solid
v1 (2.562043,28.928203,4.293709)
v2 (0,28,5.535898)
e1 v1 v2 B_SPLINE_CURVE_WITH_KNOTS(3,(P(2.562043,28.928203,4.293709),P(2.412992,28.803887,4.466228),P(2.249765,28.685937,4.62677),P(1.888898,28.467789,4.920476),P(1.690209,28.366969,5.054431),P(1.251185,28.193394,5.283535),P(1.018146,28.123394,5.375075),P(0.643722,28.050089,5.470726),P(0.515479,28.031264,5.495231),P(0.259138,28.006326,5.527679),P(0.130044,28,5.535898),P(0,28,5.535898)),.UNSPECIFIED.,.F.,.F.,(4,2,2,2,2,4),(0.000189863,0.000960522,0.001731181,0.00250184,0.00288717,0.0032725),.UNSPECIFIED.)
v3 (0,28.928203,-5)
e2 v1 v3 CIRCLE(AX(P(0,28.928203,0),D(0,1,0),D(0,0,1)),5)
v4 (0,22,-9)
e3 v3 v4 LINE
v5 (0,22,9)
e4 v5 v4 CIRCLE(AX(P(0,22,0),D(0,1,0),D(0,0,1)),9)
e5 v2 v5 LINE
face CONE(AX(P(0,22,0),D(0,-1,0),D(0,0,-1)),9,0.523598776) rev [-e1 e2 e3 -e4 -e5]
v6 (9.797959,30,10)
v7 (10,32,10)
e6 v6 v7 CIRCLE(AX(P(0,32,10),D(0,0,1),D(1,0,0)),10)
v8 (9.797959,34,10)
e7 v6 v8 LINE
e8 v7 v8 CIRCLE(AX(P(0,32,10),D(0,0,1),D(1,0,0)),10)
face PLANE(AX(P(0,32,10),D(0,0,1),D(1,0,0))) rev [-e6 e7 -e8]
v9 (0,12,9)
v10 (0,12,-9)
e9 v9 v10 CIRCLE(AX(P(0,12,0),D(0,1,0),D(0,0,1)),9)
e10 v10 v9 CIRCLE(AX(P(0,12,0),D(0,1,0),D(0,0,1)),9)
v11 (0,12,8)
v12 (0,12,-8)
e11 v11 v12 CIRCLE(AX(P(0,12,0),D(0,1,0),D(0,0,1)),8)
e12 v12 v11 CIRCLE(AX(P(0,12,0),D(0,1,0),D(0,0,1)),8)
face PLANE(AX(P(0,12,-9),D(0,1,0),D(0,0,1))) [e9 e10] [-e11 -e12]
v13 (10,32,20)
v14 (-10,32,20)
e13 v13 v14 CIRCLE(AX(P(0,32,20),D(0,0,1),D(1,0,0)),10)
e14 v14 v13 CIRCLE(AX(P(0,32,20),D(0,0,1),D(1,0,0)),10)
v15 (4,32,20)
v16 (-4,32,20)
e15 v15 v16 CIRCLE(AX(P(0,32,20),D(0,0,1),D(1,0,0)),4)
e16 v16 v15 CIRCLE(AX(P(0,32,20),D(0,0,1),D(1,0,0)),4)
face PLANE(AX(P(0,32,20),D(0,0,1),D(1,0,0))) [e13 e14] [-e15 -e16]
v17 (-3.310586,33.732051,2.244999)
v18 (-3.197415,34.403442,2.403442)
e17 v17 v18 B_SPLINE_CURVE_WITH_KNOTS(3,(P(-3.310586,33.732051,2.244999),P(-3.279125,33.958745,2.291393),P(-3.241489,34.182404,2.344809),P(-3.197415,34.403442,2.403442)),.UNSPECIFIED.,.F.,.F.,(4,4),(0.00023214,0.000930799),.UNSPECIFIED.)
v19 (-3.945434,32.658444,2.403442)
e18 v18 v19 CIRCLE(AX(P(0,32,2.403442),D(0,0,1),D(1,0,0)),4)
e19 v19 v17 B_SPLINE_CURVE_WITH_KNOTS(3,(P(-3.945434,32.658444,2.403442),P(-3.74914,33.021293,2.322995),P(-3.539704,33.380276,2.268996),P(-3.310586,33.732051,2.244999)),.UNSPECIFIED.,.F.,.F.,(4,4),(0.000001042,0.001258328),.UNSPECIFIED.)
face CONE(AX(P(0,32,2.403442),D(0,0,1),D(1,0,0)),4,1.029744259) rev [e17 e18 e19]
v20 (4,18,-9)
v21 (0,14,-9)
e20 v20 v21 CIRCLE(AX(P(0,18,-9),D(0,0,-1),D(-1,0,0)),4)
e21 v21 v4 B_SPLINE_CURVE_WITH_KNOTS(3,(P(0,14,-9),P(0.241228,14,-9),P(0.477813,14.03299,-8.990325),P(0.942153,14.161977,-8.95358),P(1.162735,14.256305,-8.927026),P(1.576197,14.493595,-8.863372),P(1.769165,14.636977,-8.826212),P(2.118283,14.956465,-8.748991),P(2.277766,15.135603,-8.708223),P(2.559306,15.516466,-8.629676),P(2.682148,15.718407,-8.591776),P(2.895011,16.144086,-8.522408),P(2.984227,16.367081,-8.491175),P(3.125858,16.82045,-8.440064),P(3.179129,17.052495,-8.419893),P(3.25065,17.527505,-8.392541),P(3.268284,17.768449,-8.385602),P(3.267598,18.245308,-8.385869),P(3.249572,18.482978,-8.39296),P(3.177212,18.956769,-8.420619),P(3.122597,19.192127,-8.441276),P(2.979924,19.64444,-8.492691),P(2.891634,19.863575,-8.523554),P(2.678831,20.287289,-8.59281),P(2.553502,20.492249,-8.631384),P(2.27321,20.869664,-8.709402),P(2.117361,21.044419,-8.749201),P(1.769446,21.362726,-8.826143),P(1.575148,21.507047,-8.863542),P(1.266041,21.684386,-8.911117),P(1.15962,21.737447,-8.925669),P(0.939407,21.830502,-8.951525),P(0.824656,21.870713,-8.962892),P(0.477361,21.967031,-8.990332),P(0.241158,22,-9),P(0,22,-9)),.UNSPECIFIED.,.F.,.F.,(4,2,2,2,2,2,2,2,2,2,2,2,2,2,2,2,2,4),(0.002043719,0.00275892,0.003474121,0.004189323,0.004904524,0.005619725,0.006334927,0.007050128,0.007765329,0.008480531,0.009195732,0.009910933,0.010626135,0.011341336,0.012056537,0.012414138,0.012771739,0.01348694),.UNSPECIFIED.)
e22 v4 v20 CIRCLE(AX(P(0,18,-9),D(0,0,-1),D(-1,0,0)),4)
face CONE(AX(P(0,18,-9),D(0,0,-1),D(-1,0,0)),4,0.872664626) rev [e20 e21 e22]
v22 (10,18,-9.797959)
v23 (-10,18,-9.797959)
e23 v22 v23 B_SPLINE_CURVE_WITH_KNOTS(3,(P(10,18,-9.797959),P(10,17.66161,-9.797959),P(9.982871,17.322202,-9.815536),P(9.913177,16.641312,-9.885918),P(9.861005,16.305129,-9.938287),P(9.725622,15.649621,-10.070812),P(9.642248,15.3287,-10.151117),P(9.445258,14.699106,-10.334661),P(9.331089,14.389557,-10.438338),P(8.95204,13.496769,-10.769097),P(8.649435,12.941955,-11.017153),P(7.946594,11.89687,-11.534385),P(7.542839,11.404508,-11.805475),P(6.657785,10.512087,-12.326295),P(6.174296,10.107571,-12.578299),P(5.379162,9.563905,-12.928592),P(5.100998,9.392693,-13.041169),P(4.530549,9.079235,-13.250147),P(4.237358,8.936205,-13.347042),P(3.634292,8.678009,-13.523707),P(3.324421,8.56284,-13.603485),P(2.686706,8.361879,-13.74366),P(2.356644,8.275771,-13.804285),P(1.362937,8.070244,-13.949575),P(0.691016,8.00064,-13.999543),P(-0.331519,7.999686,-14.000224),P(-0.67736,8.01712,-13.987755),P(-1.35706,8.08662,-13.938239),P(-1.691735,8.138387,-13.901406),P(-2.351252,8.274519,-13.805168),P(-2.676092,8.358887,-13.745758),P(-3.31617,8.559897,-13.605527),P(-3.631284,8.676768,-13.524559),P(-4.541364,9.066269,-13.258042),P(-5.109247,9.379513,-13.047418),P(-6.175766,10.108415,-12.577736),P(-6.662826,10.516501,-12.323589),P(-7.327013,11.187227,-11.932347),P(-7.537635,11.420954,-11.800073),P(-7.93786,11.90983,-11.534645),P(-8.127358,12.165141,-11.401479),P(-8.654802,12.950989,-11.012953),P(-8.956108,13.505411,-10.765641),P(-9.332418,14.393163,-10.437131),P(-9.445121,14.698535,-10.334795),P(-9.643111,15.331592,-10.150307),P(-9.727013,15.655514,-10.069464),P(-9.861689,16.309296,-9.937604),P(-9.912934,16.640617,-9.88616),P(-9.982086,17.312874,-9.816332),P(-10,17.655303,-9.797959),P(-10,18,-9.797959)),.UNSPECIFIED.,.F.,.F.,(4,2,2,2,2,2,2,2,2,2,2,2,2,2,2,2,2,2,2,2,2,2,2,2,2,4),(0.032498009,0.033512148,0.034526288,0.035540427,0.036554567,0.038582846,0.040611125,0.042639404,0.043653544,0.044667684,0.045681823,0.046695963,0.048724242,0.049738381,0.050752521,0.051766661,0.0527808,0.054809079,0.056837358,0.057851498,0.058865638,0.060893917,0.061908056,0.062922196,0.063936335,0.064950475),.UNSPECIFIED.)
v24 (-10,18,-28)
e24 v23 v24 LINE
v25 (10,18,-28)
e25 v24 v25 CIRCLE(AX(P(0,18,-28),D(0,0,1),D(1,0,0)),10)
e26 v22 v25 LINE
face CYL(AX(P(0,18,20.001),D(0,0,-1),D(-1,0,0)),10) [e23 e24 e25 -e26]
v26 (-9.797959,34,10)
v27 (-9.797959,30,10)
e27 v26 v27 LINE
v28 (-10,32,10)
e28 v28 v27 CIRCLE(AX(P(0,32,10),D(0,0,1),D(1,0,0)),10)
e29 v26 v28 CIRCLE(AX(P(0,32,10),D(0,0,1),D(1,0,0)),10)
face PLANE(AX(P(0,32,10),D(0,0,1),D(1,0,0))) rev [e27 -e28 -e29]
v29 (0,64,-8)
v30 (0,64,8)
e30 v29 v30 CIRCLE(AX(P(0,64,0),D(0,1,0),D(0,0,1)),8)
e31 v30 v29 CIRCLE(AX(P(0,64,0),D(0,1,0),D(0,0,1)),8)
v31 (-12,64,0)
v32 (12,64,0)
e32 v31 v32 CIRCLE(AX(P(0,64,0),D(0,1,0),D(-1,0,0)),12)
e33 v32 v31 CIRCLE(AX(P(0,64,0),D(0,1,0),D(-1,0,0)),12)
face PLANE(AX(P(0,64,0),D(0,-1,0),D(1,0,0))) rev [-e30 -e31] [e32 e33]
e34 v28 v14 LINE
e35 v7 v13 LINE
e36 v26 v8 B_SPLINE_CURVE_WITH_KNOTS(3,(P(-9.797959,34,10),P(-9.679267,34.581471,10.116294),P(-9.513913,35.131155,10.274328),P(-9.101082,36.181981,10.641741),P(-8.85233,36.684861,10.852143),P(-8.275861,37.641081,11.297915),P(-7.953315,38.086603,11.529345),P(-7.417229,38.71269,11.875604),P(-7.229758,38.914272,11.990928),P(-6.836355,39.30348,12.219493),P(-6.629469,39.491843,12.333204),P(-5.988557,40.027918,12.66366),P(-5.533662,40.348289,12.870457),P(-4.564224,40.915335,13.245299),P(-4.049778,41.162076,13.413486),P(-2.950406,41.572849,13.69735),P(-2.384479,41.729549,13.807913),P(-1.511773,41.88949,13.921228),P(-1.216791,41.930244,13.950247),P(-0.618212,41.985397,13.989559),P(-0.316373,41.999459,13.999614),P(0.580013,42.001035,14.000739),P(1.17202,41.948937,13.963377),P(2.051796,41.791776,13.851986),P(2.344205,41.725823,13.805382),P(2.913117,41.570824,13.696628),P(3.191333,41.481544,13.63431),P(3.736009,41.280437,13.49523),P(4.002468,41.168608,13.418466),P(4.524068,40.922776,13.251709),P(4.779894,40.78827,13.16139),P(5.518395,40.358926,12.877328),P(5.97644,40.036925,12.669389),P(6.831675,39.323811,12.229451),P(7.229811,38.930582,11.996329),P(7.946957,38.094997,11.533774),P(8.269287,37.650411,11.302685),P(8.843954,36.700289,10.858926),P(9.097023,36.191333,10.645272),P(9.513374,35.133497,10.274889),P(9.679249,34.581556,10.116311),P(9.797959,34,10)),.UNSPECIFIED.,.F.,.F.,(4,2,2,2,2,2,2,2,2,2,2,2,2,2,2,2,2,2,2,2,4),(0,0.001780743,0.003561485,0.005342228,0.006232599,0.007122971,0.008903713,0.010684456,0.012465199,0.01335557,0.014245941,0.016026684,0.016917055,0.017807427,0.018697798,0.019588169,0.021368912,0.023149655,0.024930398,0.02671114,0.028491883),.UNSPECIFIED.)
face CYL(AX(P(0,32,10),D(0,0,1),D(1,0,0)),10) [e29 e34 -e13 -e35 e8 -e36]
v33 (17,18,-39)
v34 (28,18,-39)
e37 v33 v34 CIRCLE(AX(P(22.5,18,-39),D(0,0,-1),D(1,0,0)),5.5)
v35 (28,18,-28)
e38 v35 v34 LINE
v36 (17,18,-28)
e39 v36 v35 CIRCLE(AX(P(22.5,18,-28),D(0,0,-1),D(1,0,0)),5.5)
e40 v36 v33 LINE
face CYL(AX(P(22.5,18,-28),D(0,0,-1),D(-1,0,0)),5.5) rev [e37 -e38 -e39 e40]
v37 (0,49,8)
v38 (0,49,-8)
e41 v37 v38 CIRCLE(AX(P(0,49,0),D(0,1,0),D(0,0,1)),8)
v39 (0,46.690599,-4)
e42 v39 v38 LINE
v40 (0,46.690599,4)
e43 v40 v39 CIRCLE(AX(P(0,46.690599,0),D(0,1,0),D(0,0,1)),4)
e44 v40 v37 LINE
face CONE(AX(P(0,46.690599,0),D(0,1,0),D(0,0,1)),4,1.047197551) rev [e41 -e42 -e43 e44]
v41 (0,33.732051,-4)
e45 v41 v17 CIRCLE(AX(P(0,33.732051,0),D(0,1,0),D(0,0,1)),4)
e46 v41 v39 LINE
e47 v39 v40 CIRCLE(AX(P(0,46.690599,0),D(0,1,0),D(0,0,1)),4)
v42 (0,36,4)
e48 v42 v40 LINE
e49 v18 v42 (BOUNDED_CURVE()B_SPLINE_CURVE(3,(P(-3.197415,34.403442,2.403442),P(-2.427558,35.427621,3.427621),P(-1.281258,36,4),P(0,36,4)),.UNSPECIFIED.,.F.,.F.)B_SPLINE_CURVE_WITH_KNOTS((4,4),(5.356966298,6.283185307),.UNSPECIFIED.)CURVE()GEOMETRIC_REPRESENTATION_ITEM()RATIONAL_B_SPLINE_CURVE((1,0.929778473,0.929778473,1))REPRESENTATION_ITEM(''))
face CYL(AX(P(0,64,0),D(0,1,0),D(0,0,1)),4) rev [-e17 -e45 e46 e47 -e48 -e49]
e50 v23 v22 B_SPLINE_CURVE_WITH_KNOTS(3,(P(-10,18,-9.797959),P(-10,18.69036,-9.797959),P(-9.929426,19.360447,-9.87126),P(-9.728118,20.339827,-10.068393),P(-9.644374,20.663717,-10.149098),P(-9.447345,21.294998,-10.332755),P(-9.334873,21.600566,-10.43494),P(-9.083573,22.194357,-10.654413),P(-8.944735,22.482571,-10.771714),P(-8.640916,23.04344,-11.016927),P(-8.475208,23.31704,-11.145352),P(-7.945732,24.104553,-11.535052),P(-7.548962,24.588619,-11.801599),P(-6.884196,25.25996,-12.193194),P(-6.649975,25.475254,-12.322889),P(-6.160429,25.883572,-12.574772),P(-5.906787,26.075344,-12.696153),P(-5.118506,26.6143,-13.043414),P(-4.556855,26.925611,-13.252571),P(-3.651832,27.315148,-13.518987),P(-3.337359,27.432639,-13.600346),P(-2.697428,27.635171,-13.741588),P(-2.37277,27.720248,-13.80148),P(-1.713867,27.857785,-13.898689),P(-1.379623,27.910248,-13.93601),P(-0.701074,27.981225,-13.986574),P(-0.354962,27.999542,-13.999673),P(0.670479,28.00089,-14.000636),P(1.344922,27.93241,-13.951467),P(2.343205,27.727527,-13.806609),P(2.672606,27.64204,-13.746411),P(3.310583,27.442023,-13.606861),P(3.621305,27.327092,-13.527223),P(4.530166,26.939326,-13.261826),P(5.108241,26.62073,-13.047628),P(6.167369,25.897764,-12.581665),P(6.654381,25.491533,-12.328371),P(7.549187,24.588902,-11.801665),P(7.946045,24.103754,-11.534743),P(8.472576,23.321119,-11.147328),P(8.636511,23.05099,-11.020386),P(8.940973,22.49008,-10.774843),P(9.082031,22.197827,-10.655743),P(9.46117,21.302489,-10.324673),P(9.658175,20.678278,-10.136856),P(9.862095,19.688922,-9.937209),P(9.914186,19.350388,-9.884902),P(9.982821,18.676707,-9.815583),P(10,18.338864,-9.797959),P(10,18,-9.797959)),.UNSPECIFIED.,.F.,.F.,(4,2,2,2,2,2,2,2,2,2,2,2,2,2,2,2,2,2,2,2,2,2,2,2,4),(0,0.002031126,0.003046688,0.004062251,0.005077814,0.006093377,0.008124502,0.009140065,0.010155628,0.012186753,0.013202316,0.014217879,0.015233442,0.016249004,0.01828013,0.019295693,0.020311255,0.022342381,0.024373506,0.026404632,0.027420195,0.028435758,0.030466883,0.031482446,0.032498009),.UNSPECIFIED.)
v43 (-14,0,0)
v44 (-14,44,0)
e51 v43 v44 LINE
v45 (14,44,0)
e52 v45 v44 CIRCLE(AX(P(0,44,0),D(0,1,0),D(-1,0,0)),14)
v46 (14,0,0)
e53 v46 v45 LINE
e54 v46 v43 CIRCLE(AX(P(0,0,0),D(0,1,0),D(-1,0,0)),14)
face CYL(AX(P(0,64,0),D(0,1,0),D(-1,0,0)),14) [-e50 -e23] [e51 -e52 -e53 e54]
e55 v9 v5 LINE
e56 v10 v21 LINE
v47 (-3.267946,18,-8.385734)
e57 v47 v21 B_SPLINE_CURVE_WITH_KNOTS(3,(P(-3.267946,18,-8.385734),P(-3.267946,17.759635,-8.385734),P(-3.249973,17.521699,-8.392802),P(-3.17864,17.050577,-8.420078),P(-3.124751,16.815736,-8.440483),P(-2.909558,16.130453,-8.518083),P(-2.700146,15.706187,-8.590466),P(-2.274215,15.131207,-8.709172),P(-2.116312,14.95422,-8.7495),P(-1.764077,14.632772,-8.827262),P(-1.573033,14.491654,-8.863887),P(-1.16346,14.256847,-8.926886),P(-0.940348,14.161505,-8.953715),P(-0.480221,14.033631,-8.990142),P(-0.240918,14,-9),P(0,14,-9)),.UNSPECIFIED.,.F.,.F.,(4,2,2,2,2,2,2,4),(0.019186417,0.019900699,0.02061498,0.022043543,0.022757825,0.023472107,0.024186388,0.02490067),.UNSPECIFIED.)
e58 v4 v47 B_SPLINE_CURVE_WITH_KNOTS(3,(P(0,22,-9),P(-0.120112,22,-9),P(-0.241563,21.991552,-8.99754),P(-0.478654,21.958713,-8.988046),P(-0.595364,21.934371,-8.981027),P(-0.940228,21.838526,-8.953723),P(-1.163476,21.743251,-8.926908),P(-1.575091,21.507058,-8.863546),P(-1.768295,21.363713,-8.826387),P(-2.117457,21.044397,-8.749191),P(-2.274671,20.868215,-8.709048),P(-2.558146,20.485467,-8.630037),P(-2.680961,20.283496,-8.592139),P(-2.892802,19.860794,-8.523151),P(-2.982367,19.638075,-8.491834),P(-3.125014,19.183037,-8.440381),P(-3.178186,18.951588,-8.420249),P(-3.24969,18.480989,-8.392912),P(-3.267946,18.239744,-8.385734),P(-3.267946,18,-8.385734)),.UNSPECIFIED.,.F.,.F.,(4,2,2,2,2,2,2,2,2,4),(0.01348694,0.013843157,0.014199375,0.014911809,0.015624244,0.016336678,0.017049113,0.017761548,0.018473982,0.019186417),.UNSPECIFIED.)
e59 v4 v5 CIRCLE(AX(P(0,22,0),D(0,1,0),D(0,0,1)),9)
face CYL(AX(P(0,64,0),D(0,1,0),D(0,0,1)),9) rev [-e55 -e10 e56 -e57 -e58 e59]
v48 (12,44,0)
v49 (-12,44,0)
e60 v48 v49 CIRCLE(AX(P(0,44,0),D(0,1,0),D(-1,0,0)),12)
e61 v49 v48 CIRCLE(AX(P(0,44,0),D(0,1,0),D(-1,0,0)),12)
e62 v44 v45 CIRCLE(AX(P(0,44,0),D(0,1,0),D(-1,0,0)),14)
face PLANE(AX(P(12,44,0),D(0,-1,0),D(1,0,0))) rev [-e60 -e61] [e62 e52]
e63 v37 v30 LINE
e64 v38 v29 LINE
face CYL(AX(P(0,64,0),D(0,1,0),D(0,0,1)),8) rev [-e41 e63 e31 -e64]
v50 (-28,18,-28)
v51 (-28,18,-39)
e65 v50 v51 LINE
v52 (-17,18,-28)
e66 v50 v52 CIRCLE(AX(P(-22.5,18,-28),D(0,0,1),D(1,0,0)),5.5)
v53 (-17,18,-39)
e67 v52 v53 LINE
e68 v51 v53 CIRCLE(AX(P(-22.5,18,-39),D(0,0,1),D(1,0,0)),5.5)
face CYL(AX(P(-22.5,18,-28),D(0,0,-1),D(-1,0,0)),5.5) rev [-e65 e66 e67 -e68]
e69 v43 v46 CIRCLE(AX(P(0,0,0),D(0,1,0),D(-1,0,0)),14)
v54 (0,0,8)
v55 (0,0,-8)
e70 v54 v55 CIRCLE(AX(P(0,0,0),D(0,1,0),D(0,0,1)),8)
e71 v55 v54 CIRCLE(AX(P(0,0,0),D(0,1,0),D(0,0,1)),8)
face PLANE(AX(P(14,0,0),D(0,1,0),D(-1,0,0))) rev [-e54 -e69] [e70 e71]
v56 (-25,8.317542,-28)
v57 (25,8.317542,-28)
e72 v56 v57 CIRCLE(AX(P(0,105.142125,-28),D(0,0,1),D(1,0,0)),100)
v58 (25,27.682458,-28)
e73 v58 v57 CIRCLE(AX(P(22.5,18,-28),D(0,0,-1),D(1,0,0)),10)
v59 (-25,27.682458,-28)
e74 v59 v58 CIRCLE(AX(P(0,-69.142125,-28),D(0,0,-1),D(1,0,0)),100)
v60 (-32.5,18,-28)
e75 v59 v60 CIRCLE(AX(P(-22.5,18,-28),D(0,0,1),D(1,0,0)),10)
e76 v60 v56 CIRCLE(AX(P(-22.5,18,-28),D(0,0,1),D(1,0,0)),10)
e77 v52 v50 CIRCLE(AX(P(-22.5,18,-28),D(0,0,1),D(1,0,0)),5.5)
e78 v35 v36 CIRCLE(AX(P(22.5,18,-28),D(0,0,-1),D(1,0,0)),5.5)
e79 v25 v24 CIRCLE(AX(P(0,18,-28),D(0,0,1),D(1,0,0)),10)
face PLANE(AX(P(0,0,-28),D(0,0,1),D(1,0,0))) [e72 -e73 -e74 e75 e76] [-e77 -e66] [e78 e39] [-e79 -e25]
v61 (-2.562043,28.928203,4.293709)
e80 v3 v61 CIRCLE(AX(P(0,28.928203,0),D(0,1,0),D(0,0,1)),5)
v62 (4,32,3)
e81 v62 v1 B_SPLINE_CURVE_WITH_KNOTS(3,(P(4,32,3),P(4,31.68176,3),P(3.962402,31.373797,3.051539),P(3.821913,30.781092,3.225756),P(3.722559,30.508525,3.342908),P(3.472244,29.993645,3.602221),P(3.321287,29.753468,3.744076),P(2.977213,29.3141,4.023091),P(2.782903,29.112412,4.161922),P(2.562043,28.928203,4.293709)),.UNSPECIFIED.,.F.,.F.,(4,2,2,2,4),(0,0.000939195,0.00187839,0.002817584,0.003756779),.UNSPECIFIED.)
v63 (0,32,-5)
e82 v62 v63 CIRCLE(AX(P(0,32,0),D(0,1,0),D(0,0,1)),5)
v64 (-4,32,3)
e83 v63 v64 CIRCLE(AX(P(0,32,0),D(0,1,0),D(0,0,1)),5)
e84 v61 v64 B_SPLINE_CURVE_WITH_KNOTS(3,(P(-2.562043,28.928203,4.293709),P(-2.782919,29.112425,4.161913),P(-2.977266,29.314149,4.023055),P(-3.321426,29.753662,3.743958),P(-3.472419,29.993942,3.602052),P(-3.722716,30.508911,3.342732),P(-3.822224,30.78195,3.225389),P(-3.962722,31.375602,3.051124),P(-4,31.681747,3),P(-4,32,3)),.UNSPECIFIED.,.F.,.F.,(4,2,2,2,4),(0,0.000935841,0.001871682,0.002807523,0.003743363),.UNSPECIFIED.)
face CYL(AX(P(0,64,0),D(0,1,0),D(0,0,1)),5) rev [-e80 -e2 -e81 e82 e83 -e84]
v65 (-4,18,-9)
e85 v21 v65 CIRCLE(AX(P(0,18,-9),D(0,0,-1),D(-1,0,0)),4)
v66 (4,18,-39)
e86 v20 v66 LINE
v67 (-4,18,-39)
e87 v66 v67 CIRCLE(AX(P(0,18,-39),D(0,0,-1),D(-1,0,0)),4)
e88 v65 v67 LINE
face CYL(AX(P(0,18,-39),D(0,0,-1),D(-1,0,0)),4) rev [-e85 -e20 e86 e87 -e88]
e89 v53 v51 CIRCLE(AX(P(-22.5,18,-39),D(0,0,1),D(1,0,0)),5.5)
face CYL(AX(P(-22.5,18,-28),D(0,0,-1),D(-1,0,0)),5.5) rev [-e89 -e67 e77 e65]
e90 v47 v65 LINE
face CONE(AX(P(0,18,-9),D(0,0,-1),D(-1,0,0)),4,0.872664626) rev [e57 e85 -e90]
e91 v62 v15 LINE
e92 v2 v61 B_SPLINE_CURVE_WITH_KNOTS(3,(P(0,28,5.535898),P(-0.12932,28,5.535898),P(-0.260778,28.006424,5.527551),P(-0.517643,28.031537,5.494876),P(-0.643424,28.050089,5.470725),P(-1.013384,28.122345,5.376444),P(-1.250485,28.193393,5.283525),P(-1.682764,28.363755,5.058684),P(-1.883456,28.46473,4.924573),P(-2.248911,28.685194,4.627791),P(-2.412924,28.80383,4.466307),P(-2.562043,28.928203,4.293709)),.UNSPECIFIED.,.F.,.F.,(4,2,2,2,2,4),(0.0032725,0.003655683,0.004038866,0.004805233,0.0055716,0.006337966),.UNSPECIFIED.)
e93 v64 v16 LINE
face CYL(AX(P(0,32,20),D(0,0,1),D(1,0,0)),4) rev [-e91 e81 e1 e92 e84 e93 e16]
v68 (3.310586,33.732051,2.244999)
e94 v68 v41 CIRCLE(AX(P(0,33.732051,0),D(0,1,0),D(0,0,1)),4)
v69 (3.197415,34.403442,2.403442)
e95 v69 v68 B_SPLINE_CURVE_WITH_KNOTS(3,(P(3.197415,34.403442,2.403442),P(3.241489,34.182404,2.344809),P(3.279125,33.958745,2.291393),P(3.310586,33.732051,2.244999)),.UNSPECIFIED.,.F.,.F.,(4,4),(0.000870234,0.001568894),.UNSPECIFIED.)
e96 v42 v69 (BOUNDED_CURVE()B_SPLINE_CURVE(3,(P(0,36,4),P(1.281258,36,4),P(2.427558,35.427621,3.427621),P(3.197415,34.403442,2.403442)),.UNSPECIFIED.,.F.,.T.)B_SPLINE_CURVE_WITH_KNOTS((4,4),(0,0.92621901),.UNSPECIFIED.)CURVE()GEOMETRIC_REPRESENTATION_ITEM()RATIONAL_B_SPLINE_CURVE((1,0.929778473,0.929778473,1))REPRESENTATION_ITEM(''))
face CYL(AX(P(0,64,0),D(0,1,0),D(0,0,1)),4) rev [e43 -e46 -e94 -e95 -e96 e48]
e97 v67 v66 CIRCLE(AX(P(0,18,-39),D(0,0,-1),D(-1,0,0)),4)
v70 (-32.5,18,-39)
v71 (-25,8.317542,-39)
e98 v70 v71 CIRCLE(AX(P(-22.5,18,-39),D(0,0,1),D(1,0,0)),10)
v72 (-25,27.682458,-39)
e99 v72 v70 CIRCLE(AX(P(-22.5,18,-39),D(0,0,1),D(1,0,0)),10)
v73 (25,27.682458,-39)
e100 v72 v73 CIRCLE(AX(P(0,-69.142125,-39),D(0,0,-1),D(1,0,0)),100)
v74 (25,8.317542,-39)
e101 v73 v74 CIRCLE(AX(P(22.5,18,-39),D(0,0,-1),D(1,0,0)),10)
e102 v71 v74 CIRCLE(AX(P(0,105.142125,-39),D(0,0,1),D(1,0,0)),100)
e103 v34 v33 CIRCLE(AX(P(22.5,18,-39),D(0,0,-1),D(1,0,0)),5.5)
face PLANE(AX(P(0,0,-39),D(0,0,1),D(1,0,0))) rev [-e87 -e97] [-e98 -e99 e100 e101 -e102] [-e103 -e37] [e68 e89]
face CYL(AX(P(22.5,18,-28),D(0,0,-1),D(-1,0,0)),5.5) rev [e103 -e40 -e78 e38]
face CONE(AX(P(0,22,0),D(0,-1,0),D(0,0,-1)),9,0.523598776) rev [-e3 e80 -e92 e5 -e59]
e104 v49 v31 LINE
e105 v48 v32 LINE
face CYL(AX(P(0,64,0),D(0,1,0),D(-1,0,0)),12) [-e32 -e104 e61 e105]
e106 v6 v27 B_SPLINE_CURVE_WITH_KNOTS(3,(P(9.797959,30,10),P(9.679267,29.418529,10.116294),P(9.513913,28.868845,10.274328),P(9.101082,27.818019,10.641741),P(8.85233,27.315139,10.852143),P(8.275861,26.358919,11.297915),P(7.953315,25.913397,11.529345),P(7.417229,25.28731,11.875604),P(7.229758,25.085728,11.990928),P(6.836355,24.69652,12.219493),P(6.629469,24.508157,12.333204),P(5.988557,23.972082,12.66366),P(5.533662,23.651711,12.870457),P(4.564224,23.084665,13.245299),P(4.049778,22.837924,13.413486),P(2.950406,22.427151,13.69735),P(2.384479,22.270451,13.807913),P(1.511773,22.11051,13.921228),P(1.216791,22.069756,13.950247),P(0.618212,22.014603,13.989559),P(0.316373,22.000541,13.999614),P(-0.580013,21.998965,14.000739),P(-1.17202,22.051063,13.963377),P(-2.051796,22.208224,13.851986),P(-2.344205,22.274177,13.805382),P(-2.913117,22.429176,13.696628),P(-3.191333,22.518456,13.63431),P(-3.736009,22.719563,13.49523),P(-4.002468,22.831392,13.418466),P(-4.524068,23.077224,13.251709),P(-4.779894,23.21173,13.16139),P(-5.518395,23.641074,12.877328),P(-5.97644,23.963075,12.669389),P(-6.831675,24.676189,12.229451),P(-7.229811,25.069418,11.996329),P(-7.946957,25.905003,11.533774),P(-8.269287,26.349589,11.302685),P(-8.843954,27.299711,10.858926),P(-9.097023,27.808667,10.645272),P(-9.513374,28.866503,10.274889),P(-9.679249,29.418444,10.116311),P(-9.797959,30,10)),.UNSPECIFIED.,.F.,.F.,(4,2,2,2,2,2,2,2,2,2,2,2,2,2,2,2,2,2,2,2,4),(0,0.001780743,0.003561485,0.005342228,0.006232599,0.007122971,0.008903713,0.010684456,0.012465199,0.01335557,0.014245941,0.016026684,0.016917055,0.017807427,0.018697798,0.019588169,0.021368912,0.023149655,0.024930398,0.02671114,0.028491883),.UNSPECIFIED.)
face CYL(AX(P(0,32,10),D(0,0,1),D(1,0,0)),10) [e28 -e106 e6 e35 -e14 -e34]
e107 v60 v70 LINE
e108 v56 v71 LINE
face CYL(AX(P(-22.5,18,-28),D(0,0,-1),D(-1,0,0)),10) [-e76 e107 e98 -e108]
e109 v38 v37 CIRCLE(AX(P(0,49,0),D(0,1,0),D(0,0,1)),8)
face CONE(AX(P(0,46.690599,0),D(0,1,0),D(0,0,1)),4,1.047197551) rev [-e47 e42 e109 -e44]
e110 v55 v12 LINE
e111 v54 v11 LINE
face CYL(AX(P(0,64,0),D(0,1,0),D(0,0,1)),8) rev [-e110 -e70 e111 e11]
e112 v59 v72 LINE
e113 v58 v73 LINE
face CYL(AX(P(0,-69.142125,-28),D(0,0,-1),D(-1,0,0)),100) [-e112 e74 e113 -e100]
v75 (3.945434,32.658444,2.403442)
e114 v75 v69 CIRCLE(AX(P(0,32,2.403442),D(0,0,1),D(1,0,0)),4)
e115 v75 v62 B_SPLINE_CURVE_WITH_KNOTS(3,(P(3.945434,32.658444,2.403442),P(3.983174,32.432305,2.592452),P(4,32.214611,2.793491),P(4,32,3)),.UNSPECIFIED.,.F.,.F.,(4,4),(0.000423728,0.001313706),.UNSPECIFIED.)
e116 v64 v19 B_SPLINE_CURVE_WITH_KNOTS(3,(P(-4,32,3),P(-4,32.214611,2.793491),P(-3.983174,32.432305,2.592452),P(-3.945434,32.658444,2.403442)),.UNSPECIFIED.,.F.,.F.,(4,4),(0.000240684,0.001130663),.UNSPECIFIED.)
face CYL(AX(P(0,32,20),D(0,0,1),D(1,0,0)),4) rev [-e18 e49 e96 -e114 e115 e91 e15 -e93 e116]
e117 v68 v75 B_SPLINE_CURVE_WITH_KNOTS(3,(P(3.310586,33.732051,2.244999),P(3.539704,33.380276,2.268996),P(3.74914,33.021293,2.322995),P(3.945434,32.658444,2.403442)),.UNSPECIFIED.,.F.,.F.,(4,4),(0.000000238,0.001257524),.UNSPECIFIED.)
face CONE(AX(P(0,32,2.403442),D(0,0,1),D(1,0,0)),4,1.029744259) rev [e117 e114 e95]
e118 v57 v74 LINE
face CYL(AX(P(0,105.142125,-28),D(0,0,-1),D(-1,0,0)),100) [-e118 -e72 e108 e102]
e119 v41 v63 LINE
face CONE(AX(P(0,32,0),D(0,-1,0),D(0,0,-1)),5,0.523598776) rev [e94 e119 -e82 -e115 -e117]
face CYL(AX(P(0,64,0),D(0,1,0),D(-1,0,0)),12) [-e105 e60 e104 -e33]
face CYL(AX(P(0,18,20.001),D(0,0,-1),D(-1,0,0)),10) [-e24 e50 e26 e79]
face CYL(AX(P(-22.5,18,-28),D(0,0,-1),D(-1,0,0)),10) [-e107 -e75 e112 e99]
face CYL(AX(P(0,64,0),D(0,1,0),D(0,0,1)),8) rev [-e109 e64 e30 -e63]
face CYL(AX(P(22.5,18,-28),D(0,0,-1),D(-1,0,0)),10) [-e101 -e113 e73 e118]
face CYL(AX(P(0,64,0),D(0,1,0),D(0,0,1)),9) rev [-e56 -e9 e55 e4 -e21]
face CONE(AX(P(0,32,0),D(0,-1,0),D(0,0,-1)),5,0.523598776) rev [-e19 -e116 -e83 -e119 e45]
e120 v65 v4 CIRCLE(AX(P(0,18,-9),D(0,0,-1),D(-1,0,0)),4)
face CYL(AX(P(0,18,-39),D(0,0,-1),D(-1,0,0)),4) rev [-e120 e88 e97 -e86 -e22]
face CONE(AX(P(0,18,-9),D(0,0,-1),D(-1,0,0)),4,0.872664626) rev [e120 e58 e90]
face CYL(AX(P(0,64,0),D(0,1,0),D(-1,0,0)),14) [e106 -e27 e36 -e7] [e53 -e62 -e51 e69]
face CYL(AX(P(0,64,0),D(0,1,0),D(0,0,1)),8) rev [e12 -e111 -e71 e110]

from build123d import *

# Parameters (mm, degrees)
SIDE_PORT_BOSS_SKETCH_R            = 10
SIDE_PORT_BOSS_DEPTH               = 10
MOUNTING_EAR_SKETCH_R              = 5.5
MOUNTING_EAR_DEPTH                 = 11
EAR_HUB_BOSS_REACH                 = 88.35
EAR_HUB_BOSS_END_RADIUS            = 14
EAR_HUB_SKETCH_R                   = 10
EAR_HOLE_8_D                       = 8
EAR_HOLE_8_DEPTH                   = 30
EAR_HOLE_8_TIP                     = 3.356398525
SIDE_PORT_TAPPED_HOLE_M8X1_0_D     = 8
SIDE_PORT_TAPPED_HOLE_M8X1_0_DEPTH = 17.596557524
SIDE_PORT_TAPPED_HOLE_M8X1_0_TIP   = 2.403442476


with BuildPart() as part:
    # Main Body Profile Sketch → Main Body Revolve (revolve)
    with BuildSketch(Plane.XY, mode=Mode.PRIVATE) as main_body_revolve_sk:
        Polygon((0, 64), (12, 64), (12, 44), (14, 44), (14, 0), (0, 0), align=None)
    revolve(main_body_revolve_sk.sketch.rotate(Axis((0, 64, 0), (0, -1, 0)), 180), axis=Axis((0, 64, 0), (0, -1, 0)))

    # Side Port Boss Sketch → Side Port Boss (add)
    with BuildSketch(Plane.XY.offset(20)):
        with Locations((0, 32)):
            Circle(SIDE_PORT_BOSS_SKETCH_R)
    extrude(amount=-SIDE_PORT_BOSS_DEPTH)



with BuildPart() as body_2:
    # Mounting Ear Sketch → Mounting Ear (new body)
    # profile 1 of 6: a face of its own
    with BuildSketch(Plane.XY.offset(-39)):
        with BuildLine():
            Line((0, 14), (0, 5.14212529))
            ThreePointArc((0, 5.14212529), (12.600429248, 5.939155663), (25, 8.317541634))
            ThreePointArc((25, 8.317541634), (32.5, 18), (25, 27.682458366))
            ThreePointArc((25, 27.682458366), (12.600429248, 30.060844337), (0, 30.85787471))
            Line((0, 30.85787471), (0, 22))
            ThreePointArc((0, 22), (2.828427125, 20.828427125), (4, 18))
            ThreePointArc((4, 18), (2.828427125, 15.171572875), (0, 14))
        make_face()
        with Locations((22.5, 18)):
            Circle(MOUNTING_EAR_SKETCH_R, mode=Mode.SUBTRACT)
    # profile 2 of 6: a face of its own
    with BuildSketch(Plane.XY.offset(-39)):
        with BuildLine():
            ThreePointArc((-25, 8.317541634), (-12.600429248, 5.939155663), (0, 5.14212529))
            Line((0, 5.14212529), (0, 14))
            ThreePointArc((0, 14), (-4, 18), (0, 22))
            Line((0, 22), (0, 30.85787471))
            ThreePointArc((0, 30.85787471), (-12.600429248, 30.060844337), (-25, 27.682458366))
            ThreePointArc((-25, 27.682458366), (-32.5, 18), (-25, 8.317541634))
        make_face()
        with Locations((-22.5, 18)):
            Circle(MOUNTING_EAR_SKETCH_R, mode=Mode.SUBTRACT)
    # profile 3 of 6: a face of its own
    with BuildSketch(Plane.XY.offset(-39)):
        with BuildLine():
            ThreePointArc((0, 22), (-4, 18), (0, 14))
            Line((0, 14), (0, 22))
        make_face()
    # profile 4 of 6: a face of its own
    with BuildSketch(Plane.XY.offset(-39)):
        with BuildLine():
            Line((0, 22), (0, 14))
            ThreePointArc((0, 14), (2.828427125, 15.171572875), (4, 18))
            ThreePointArc((4, 18), (2.828427125, 20.828427125), (0, 22))
        make_face()
    # profile 5 of 6: a face of its own
    with BuildSketch(Plane.XY.offset(-39)):
        with BuildLine():
            ThreePointArc((0, 22), (-4, 18), (0, 14))
            Line((0, 14), (0, 22))
        make_face()
    # profile 6 of 6: a face of its own
    with BuildSketch(Plane.XY.offset(-39)):
        with BuildLine():
            Line((0, 22), (0, 14))
            ThreePointArc((0, 14), (2.828427125, 15.171572875), (4, 18))
            ThreePointArc((4, 18), (2.828427125, 20.828427125), (0, 22))
        make_face()
    extrude(amount=MOUNTING_EAR_DEPTH)


with BuildPart() as part_1:
    add(part.part)

    add(body_2.part)  # Ear Hub Boss merges body 2
    # Ear Hub Boss: up to this cylinder (the profile starts outside it)
    ear_hub_boss_end = Plane(origin=(0, 18, 0), z_dir=(0, 1, 0)) * Cylinder(EAR_HUB_BOSS_END_RADIUS, 205.7, mode=Mode.PRIVATE)
    # Ear Hub Sketch → Ear Hub Boss (add, up to the surface)
    with BuildSketch(Plane.XY.offset(-28), mode=Mode.PRIVATE) as ear_hub_boss_sk1:
        with Locations(Location((0, 18, 0), (0, 0, 180))):
            Circle(EAR_HUB_SKETCH_R)
    ear_hub_boss_tool1 = extrude(ear_hub_boss_sk1.sketch, amount=EAR_HUB_BOSS_REACH, mode=Mode.PRIVATE) - ear_hub_boss_end
    add(ear_hub_boss_tool1.solids().sort_by_distance((0, 18, -28))[0])

    # Bore Profile Sketch → Bore Revolve Cut (revolve, cut)
    with BuildSketch(Plane(origin=(0, 0, 0), x_dir=(0, 0, -1), z_dir=(1, 0, 0)), mode=Mode.PRIVATE) as bore_revolve_cut_sk:
        Polygon((0, 64), (8, 64), (8, 49), (4, 46.690598923), (4, 33.732050808), (5, 32), (5, 28.92820323), (9, 22), (9, 12), (8, 12), (8, 0), (0, 0), align=None)
    revolve(bore_revolve_cut_sk.sketch.rotate(Axis((0, 64, 0), (0, -1, 0)), 180), axis=Axis((0, 64, 0), (0, -1, 0)), mode=Mode.SUBTRACT)

    # Ear Hole Ø8
    with Locations(Plane(origin=(0, 0, -39), x_dir=(-1, 0, 0), z_dir=(0, 0, -1))):
        with Locations((0, 18)):
            Hole(EAR_HOLE_8_D / 2, depth=EAR_HOLE_8_DEPTH)
            with Locations((0, 0, -(EAR_HOLE_8_DEPTH + EAR_HOLE_8_TIP / 2))):  # 100° drill point
                Cone(0, EAR_HOLE_8_D / 2, EAR_HOLE_8_TIP, mode=Mode.SUBTRACT)

    # Side Port Tapped Hole M8x1.0
    with Locations(Plane.XY.offset(20)):
        with Locations((0, 32)):
            Hole(SIDE_PORT_TAPPED_HOLE_M8X1_0_D / 2, depth=SIDE_PORT_TAPPED_HOLE_M8X1_0_DEPTH)
            with Locations((0, 0, -(SIDE_PORT_TAPPED_HOLE_M8X1_0_DEPTH + SIDE_PORT_TAPPED_HOLE_M8X1_0_TIP / 2))):  # 118° drill point
                Cone(0, SIDE_PORT_TAPPED_HOLE_M8X1_0_D / 2, SIDE_PORT_TAPPED_HOLE_M8X1_0_TIP, mode=Mode.SUBTRACT)


solid = part_1.part
